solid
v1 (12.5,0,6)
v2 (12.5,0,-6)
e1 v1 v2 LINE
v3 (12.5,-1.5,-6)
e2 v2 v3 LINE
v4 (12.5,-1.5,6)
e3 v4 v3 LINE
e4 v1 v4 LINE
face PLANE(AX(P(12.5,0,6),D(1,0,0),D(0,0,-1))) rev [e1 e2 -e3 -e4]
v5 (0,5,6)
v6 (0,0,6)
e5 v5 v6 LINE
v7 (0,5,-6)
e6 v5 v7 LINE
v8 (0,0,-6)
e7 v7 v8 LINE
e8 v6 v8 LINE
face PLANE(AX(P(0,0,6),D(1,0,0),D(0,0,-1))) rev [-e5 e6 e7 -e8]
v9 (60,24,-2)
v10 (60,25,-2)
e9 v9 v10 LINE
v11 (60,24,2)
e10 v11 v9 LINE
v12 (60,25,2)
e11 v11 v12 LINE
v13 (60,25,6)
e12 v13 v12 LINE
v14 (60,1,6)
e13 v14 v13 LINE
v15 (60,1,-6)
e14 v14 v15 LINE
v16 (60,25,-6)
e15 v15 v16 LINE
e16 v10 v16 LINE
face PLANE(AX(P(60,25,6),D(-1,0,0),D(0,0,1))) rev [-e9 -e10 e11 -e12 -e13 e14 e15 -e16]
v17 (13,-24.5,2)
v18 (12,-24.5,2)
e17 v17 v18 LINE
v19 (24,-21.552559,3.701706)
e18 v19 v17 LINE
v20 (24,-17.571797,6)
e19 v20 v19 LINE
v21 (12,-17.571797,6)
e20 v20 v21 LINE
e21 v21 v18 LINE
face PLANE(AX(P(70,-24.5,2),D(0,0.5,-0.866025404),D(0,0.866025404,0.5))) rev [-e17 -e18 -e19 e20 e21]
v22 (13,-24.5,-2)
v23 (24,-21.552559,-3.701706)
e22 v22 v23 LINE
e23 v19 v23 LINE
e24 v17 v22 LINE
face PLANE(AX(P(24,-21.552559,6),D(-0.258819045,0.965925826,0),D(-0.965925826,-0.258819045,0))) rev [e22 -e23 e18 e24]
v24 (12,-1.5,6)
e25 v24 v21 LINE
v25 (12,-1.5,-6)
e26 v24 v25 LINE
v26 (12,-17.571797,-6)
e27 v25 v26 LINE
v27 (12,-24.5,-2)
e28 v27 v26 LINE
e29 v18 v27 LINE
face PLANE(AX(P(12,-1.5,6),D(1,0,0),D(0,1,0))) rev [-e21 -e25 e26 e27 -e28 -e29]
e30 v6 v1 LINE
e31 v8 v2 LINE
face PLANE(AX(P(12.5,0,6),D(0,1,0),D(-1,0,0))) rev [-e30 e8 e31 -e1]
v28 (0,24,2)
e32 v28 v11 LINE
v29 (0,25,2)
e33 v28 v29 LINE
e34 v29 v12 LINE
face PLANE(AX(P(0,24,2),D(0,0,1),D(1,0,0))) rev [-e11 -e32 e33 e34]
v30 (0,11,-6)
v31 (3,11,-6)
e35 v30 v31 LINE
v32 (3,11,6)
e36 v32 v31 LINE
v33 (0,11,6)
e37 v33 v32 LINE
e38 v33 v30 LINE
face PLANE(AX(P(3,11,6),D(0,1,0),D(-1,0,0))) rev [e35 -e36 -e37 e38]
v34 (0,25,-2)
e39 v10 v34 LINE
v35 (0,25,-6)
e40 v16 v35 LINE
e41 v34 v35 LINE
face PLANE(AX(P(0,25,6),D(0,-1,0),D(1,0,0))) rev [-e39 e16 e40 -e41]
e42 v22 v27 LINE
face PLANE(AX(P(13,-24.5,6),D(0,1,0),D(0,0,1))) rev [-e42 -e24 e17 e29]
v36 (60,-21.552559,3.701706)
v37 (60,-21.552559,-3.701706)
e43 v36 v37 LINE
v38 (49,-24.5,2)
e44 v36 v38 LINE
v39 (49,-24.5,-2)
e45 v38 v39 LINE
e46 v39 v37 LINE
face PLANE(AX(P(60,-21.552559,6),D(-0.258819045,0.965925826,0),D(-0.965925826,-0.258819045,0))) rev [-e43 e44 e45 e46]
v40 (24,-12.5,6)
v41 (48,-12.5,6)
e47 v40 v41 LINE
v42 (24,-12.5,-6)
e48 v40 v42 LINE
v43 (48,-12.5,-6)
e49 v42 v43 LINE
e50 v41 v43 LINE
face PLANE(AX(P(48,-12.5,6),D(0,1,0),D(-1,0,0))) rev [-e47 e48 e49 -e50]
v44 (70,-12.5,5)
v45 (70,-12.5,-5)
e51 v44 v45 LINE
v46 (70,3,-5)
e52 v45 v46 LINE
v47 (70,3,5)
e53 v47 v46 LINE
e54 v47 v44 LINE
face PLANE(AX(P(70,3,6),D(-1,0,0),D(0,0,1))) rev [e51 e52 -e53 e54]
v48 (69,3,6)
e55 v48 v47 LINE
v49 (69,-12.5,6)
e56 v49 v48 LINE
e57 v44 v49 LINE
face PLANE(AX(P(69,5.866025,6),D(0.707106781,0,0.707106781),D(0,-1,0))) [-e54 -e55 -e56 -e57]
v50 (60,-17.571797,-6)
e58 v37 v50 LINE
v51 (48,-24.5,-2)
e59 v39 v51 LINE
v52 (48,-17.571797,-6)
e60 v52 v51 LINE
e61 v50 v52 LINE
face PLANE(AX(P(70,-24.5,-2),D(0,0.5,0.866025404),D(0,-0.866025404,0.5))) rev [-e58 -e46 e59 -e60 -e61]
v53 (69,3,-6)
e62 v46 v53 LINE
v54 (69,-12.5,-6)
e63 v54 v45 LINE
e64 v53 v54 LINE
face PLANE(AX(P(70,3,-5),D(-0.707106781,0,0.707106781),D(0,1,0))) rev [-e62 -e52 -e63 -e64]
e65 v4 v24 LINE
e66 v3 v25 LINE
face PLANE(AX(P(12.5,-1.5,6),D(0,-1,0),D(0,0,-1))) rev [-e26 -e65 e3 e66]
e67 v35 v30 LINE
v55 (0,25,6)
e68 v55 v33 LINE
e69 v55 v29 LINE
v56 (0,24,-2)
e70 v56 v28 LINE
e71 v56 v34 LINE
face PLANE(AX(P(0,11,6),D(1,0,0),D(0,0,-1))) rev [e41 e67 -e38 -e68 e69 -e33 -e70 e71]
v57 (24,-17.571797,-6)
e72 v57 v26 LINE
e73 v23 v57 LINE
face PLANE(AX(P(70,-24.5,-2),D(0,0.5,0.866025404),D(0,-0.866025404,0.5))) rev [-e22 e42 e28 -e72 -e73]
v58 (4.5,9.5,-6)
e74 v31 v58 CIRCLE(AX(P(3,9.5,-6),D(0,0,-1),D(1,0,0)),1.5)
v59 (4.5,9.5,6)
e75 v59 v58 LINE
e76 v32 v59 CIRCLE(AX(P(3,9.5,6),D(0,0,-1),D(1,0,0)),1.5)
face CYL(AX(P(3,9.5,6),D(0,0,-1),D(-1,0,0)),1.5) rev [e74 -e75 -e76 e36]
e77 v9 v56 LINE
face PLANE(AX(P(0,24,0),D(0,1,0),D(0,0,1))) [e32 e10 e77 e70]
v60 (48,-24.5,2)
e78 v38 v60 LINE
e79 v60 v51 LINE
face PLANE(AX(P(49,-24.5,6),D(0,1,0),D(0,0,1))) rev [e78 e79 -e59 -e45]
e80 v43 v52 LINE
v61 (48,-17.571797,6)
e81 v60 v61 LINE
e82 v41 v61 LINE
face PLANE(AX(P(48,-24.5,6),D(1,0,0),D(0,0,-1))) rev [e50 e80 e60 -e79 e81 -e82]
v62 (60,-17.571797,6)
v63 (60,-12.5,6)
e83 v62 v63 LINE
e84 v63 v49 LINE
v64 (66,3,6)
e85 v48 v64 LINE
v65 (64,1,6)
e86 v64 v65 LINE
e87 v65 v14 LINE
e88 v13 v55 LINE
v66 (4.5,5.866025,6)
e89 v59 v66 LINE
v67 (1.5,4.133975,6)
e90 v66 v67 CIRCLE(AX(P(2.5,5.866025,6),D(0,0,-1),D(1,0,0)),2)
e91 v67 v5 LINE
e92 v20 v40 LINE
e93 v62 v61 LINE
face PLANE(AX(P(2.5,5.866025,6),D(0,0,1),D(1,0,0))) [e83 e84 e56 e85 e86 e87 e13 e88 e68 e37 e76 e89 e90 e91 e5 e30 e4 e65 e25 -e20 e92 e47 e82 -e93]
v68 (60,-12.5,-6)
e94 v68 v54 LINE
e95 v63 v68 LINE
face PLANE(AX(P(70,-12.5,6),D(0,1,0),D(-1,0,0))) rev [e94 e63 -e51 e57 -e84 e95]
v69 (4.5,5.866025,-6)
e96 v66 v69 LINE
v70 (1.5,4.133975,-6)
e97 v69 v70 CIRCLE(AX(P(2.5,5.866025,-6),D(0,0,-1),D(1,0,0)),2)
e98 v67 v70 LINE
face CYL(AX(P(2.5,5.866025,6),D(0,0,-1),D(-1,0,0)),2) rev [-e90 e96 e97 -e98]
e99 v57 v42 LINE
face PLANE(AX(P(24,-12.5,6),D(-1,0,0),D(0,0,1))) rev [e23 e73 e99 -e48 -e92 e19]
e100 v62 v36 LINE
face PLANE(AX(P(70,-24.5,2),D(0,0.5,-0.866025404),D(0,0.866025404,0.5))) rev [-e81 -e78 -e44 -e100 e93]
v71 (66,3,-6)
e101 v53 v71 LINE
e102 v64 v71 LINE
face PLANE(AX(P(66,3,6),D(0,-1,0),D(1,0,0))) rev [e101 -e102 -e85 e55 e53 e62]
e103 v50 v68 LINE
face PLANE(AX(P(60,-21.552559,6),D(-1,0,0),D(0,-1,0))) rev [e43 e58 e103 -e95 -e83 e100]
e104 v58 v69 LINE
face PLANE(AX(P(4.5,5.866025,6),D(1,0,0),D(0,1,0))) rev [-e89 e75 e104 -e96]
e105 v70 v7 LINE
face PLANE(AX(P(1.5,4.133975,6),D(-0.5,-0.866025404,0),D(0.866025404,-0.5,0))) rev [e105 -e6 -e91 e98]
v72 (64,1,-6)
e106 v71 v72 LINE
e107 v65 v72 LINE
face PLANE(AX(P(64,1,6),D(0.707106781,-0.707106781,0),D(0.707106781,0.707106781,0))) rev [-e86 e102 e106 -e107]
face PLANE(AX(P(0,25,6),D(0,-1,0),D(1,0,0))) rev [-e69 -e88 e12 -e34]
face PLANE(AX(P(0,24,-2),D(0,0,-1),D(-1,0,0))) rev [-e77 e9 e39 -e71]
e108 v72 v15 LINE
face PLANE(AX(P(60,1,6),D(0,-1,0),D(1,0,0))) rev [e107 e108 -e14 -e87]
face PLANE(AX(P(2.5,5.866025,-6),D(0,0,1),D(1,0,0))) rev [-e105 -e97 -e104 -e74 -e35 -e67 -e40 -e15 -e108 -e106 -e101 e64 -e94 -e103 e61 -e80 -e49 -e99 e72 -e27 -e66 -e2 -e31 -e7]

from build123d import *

# Parameters (mm, degrees)
EXTRUDE_1_DEPTH     = 6
CUT_EXTRUDE_1_DEPTH = 64.442887702
SKETCH_3_W          = 60
SKETCH_3_H          = 4
CUT_EXTRUDE_2_DEPTH = 1
CHAMFER_1_SIZE      = 1


with BuildPart() as part:
    # 草图1 → 凸台-拉伸1 (new, symmetric)
    with BuildSketch(Plane.XY):
        with BuildLine():
            Line((0, 0), (0, 5))
            Line((0, 5), (1.5, 4.133974596))
            ThreePointArc((1.5, 4.133974596), (3.5, 4.133974596), (4.5, 5.866025404))
            Line((4.5, 5.866025404), (4.5, 9.5))
            ThreePointArc((4.5, 9.5), (4.060660172, 10.560660172), (3, 11))
            Line((3, 11), (0, 11))
            Line((0, 11), (0, 25))
            Line((0, 25), (60, 25))
            Line((60, 25), (60, 1))
            Line((60, 1), (64, 1))
            Line((64, 1), (66, 3))
            Line((66, 3), (70, 3))
            Line((70, 3), (70, -12.5))
            Line((70, -12.5), (60, -12.5))
            Line((60, -12.5), (60, -21.552558883))
            Line((60, -21.552558883), (49, -24.5))
            Line((49, -24.5), (48, -24.5))
            Line((48, -24.5), (48, -12.5))
            Line((48, -12.5), (24, -12.5))
            Line((24, -12.5), (24, -21.552558883))
            Line((24, -21.552558883), (13, -24.5))
            Line((13, -24.5), (12, -24.5))
            Line((12, -24.5), (12, -1.5))
            Line((12, -1.5), (12.5, -1.5))
            Line((12.5, -1.5), (12.5, 0))
            Line((12.5, 0), (0, 0))
        make_face()
    extrude(amount=EXTRUDE_1_DEPTH, both=True)

    # 草图2 → 切除-拉伸1 (cut, through all)
    with BuildSketch(Plane.ZY.offset(-12)):
        Polygon((6, -17.57179677), (6, -29.5), (-6, -29.5), (-6, -17.57179677), (-2, -24.5), (2, -24.5), align=None)
    extrude(amount=-CUT_EXTRUDE_1_DEPTH, mode=Mode.SUBTRACT)

    # 草图3 → 切除-拉伸2 (cut)
    with BuildSketch(Plane(origin=(0, 25, 0), x_dir=(1, 0, 0), z_dir=(0, 1, 0))):
        with Locations((30, 0)):
            Rectangle(SKETCH_3_W, SKETCH_3_H)
    extrude(amount=-CUT_EXTRUDE_2_DEPTH, mode=Mode.SUBTRACT)

    # 倒角1
    chamfer_1_edges = [part.edges().sort_by_distance(p)[0] for p in [
        (70, -4.75, -6),
        (70, -4.75, 6),
    ]]
    chamfer(chamfer_1_edges, length=CHAMFER_1_SIZE)


solid = part.part
